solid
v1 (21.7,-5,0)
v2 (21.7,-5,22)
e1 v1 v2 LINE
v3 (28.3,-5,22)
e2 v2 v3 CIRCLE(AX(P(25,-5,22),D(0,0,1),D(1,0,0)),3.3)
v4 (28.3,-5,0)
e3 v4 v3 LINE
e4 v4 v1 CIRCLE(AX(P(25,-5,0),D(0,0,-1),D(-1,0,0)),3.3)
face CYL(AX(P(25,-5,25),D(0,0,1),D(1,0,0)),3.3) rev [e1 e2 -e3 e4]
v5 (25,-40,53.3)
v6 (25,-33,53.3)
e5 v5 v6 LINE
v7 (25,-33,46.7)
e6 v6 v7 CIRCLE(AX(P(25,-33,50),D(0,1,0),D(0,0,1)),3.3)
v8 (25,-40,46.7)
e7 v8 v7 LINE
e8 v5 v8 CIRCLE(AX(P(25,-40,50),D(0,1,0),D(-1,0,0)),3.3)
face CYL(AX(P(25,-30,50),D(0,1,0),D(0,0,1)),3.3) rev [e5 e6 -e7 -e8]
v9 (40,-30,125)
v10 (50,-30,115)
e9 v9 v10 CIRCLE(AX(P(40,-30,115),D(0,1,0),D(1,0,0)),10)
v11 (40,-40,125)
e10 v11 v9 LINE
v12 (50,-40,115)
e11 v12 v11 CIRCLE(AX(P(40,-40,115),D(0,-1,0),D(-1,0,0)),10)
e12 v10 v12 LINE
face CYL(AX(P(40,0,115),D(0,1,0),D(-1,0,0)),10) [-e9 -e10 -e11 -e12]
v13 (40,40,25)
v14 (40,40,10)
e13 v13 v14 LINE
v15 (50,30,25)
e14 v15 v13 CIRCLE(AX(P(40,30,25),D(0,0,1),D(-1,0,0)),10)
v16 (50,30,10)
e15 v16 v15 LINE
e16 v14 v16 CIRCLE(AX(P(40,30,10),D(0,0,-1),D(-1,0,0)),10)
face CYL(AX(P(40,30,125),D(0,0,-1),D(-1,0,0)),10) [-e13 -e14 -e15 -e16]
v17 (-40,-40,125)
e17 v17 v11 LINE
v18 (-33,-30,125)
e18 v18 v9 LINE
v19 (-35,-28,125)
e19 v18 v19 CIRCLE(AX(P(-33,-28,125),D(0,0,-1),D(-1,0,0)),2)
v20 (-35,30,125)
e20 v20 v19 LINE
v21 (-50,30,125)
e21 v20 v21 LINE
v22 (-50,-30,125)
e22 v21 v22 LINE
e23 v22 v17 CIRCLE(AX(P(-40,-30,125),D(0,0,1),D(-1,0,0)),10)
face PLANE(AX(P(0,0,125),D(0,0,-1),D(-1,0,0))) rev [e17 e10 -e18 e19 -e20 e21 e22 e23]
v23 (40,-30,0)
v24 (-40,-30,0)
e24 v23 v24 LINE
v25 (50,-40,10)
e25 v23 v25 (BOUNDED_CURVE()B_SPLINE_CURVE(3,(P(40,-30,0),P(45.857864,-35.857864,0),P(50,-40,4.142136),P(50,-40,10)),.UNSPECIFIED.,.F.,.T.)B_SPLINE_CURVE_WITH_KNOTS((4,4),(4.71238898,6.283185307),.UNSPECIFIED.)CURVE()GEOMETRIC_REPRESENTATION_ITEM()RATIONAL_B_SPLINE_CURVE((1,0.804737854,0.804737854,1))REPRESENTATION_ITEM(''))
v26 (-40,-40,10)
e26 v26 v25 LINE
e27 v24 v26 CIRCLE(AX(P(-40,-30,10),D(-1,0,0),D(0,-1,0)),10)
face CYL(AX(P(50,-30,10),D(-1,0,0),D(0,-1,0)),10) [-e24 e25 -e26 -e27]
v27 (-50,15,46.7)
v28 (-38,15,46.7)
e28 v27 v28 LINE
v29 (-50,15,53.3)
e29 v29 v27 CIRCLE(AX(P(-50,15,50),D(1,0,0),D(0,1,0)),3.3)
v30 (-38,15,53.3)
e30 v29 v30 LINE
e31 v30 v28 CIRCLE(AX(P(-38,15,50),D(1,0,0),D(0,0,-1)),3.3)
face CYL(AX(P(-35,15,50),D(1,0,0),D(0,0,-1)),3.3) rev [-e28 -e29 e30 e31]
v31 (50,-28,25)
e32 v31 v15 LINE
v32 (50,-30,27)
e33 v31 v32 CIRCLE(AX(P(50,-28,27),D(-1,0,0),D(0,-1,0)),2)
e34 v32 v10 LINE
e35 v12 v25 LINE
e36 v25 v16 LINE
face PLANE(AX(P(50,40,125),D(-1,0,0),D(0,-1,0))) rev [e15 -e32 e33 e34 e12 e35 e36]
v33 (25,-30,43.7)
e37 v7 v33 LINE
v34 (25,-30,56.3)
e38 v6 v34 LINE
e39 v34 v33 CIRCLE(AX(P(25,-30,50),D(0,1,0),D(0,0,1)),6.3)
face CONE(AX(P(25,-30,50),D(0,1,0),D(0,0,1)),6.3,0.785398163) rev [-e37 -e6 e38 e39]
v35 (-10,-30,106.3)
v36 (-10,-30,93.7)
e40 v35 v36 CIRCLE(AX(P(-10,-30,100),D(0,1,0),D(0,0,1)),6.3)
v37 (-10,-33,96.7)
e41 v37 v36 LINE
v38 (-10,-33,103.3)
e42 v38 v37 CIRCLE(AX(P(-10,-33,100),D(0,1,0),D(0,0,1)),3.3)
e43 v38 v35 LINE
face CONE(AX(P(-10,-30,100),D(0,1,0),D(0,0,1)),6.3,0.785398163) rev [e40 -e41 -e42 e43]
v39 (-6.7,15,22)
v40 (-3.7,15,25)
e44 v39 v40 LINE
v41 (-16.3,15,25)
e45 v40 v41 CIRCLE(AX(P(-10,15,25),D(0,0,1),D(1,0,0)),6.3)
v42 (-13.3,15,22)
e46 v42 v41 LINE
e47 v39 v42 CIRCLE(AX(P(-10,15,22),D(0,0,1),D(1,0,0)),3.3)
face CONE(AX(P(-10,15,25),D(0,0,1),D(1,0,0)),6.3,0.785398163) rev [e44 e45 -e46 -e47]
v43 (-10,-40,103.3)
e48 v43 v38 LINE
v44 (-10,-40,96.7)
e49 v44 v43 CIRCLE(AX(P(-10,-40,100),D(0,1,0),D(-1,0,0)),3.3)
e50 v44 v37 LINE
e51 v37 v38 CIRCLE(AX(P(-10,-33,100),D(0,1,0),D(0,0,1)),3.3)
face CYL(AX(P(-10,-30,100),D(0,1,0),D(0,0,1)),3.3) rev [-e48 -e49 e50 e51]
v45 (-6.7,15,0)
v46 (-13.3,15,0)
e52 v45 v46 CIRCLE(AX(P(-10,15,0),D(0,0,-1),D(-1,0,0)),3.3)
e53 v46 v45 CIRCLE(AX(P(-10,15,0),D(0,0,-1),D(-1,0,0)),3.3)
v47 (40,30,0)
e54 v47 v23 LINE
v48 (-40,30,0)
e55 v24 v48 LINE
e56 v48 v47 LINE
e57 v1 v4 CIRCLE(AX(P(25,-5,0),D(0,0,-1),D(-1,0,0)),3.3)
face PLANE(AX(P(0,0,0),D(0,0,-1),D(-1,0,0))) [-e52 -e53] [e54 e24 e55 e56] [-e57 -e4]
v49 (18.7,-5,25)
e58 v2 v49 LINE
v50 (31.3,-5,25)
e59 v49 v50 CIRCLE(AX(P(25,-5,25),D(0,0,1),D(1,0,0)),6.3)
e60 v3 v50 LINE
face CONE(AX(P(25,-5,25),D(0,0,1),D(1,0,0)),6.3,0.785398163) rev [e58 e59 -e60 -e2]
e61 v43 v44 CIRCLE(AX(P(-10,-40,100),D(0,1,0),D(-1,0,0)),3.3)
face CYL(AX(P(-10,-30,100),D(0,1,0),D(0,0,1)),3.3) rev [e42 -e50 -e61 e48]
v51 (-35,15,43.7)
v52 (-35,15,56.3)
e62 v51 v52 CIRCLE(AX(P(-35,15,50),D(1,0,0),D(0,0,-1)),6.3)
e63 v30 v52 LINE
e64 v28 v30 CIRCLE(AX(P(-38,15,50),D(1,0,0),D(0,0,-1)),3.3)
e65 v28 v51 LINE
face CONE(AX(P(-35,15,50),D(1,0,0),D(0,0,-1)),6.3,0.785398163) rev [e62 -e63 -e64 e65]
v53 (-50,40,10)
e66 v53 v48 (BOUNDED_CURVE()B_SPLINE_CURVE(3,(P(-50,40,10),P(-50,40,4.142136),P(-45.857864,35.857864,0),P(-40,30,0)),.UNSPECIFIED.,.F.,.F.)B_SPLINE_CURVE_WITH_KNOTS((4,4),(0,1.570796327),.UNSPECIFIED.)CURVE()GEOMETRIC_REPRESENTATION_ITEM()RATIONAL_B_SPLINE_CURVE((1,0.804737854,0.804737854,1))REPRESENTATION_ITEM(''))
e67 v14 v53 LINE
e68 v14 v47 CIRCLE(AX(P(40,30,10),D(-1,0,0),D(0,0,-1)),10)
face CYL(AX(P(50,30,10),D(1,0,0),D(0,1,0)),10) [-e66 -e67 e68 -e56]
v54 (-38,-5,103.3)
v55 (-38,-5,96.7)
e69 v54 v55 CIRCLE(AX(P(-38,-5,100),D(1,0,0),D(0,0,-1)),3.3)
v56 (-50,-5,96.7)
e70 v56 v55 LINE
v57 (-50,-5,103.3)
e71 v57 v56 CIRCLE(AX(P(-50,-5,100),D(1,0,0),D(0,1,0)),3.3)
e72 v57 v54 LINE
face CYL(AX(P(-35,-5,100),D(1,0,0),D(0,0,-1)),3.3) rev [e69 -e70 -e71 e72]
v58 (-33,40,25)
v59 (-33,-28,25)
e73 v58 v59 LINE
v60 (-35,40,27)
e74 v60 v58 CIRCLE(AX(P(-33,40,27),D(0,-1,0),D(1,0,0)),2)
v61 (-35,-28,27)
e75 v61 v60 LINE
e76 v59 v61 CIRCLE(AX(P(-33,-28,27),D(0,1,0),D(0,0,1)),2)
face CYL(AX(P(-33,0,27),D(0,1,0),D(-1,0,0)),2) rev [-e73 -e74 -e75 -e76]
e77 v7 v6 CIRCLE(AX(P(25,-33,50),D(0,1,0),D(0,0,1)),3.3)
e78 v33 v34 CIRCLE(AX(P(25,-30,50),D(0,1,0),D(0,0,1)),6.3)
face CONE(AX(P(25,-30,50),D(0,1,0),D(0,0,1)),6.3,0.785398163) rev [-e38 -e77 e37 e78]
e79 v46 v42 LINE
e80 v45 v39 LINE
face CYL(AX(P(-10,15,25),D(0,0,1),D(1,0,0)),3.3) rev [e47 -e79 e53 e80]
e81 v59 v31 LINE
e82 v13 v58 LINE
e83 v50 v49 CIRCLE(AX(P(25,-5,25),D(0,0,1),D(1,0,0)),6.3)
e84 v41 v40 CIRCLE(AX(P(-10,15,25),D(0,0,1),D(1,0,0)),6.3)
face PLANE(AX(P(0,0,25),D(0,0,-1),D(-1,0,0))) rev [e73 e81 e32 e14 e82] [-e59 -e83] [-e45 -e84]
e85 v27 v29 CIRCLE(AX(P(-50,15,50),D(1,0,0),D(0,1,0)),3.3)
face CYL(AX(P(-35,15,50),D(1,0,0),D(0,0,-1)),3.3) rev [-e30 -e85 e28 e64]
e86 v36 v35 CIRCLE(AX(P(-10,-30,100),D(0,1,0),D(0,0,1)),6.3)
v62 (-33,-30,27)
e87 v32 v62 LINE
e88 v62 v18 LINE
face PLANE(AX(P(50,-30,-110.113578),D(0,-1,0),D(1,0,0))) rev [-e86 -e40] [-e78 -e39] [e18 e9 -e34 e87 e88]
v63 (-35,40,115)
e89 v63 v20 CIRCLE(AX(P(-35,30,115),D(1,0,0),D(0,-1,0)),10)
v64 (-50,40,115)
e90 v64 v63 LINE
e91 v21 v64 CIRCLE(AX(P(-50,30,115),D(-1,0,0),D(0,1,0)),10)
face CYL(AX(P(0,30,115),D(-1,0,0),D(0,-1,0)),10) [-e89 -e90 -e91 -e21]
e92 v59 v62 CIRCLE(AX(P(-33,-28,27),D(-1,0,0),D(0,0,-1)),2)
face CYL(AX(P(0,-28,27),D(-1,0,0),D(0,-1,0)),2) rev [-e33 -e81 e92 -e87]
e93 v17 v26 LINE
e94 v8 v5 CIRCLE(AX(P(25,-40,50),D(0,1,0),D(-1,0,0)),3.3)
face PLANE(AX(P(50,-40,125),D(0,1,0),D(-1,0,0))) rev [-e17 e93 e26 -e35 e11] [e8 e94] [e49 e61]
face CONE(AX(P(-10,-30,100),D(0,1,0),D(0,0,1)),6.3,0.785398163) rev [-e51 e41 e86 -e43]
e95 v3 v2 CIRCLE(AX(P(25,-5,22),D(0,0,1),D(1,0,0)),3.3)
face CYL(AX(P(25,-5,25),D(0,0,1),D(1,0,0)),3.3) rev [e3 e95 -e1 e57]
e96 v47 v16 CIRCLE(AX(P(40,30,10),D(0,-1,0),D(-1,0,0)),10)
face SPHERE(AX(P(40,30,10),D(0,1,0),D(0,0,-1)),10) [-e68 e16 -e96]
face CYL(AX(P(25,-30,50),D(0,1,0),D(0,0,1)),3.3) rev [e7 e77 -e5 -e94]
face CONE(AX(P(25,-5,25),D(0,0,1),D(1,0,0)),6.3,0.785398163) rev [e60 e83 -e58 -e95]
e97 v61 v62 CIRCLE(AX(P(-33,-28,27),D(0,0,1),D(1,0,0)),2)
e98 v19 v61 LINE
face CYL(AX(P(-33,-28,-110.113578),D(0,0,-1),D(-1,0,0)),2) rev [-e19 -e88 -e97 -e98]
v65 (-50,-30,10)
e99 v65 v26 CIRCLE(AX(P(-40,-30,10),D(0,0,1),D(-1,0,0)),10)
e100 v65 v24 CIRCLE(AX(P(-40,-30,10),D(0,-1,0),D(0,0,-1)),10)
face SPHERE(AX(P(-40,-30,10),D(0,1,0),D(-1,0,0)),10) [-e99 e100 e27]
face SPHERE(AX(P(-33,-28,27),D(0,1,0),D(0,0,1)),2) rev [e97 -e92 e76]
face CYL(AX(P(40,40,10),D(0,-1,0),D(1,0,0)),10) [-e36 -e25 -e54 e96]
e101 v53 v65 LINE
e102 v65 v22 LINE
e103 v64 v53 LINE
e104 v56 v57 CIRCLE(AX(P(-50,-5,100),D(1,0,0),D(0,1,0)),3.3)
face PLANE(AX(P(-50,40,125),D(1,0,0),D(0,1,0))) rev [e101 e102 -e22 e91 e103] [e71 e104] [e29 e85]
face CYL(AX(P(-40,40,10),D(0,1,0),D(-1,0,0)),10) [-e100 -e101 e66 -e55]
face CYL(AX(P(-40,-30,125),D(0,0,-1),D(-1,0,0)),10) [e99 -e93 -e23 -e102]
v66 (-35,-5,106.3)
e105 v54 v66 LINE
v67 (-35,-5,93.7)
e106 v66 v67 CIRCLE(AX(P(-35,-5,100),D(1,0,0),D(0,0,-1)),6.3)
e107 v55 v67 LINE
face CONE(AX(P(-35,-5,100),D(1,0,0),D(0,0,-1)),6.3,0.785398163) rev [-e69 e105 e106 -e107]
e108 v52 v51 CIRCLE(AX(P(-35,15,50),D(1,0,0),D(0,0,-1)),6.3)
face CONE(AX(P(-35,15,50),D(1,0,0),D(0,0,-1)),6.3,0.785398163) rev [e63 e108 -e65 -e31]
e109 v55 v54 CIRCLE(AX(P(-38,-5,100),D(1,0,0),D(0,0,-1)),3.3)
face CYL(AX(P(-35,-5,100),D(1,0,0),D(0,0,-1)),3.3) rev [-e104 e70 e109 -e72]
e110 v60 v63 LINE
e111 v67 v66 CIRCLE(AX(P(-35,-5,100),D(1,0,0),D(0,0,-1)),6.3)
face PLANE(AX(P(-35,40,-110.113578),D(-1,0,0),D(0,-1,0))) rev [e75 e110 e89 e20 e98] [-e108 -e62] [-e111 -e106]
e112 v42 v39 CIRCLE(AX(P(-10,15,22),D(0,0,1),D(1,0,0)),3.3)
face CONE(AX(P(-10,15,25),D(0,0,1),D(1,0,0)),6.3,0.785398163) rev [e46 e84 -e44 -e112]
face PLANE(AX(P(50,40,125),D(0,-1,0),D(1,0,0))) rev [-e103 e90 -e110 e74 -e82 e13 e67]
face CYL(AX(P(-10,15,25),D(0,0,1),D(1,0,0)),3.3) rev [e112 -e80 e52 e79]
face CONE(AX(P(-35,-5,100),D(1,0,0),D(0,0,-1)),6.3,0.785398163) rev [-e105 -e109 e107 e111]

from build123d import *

# Parameters (mm, degrees)
BRACKET_L_PROFILE_SKETCH_W                   = 100
BRACKET_L_PROFILE_SKETCH_H                   = 80
BRACKET_BODY_DEPTH                           = 125
RECTANGULAR_CUT_SKETCH_10X15_W               = 85
RECTANGULAR_CUT_SKETCH_10X15_H               = 70
RECTANGULAR_CUT_10X15_DEPTH                  = 100
COUNTERSUNK_HOLES_6XM6_D                     = 6.6
COUNTERSUNK_HOLES_6XM6_DEPTH                 = 36.017159957
COUNTERSUNK_HOLES_6XM6_CSINK_D               = 12.6
COUNTERSUNK_HOLES_6XM6_CSINK_ANGLE           = 90
COUNTERSUNK_HOLES_6XM6_TIP                   = 1.982840043
COUNTERSUNK_HOLES_6XM6_ON_FACE_2_D           = 6.6
COUNTERSUNK_HOLES_6XM6_ON_FACE_2_DEPTH       = 36.017159957
COUNTERSUNK_HOLES_6XM6_ON_FACE_2_CSINK_D     = 12.6
COUNTERSUNK_HOLES_6XM6_ON_FACE_2_CSINK_ANGLE = 90
COUNTERSUNK_HOLES_6XM6_ON_FACE_2_TIP         = 1.982840043
COUNTERSUNK_HOLES_6XM6_ON_FACE_3_D           = 6.6
COUNTERSUNK_HOLES_6XM6_ON_FACE_3_DEPTH       = 36.017159957
COUNTERSUNK_HOLES_6XM6_ON_FACE_3_CSINK_D     = 12.6
COUNTERSUNK_HOLES_6XM6_ON_FACE_3_CSINK_ANGLE = 90
COUNTERSUNK_HOLES_6XM6_ON_FACE_3_TIP         = 1.982840043
OUTER_EDGE_FILLETS_R10_R                     = 10
EDGE_FILLETS_R2_R                            = 2


with BuildPart() as part:
    # Bracket L-Profile Sketch → Bracket Body (new body)
    with BuildSketch(Plane.XY):
        Rectangle(BRACKET_L_PROFILE_SKETCH_W, BRACKET_L_PROFILE_SKETCH_H)
    extrude(amount=BRACKET_BODY_DEPTH)

    # Rectangular Cut Sketch 10x15 → Rectangular Cut 10x15 (cut)
    with BuildSketch(Plane.XY.offset(125)):
        with Locations((7.5, 5)):
            Rectangle(RECTANGULAR_CUT_SKETCH_10X15_W, RECTANGULAR_CUT_SKETCH_10X15_H)
    extrude(amount=-RECTANGULAR_CUT_10X15_DEPTH, mode=Mode.SUBTRACT)

    # Countersunk Holes 6xM6
    with Locations(Plane(origin=(-35, -5, 100), x_dir=(0, 1, 0), z_dir=(1, 0, 0))):
        with Locations((0, 0), (20, -50)):
            CounterSinkHole(COUNTERSUNK_HOLES_6XM6_D / 2, COUNTERSUNK_HOLES_6XM6_CSINK_D / 2, depth=COUNTERSUNK_HOLES_6XM6_DEPTH, counter_sink_angle=COUNTERSUNK_HOLES_6XM6_CSINK_ANGLE)
            with Locations((0, 0, -(COUNTERSUNK_HOLES_6XM6_DEPTH + COUNTERSUNK_HOLES_6XM6_TIP / 2))):  # 118° drill point
                Cone(0, COUNTERSUNK_HOLES_6XM6_D / 2, COUNTERSUNK_HOLES_6XM6_TIP, mode=Mode.SUBTRACT)

    # Countersunk Holes 6xM6 on face 2
    with Locations(Plane(origin=(-10, -30, 100), x_dir=(0, 0, 1), z_dir=(0, 1, 0))):
        with Locations((0, 0), (-50, 35)):
            CounterSinkHole(COUNTERSUNK_HOLES_6XM6_ON_FACE_2_D / 2, COUNTERSUNK_HOLES_6XM6_ON_FACE_2_CSINK_D / 2, depth=COUNTERSUNK_HOLES_6XM6_ON_FACE_2_DEPTH, counter_sink_angle=COUNTERSUNK_HOLES_6XM6_ON_FACE_2_CSINK_ANGLE)
            with Locations((0, 0, -(COUNTERSUNK_HOLES_6XM6_ON_FACE_2_DEPTH + COUNTERSUNK_HOLES_6XM6_ON_FACE_2_TIP / 2))):  # 118° drill point
                Cone(0, COUNTERSUNK_HOLES_6XM6_ON_FACE_2_D / 2, COUNTERSUNK_HOLES_6XM6_ON_FACE_2_TIP, mode=Mode.SUBTRACT)

    # Countersunk Holes 6xM6 on face 3
    with Locations(Plane(origin=(25, -5, 25), x_dir=(1, 0, 0), z_dir=(0, 0, 1))):
        with Locations((0, 0), (-35, 20)):
            CounterSinkHole(COUNTERSUNK_HOLES_6XM6_ON_FACE_3_D / 2, COUNTERSUNK_HOLES_6XM6_ON_FACE_3_CSINK_D / 2, depth=COUNTERSUNK_HOLES_6XM6_ON_FACE_3_DEPTH, counter_sink_angle=COUNTERSUNK_HOLES_6XM6_ON_FACE_3_CSINK_ANGLE)
            with Locations((0, 0, -(COUNTERSUNK_HOLES_6XM6_ON_FACE_3_DEPTH + COUNTERSUNK_HOLES_6XM6_ON_FACE_3_TIP / 2))):  # 118° drill point
                Cone(0, COUNTERSUNK_HOLES_6XM6_ON_FACE_3_D / 2, COUNTERSUNK_HOLES_6XM6_ON_FACE_3_TIP, mode=Mode.SUBTRACT)

    # Outer Edge Fillets R10
    outer_edge_fillets_r10_edges = [part.edges().sort_by_distance(p)[0] for p in [
        (50, -35, 125),
        (-42.5, 40, 125),
        (50, 40, 12.5),
        (0, 40, 0),
        (50, 0, 0),
        (0, -40, 0),
        (-50, 0, 0),
        (-50, -40, 62.5),
    ]]
    fillet(outer_edge_fillets_r10_edges, radius=OUTER_EDGE_FILLETS_R10_R)

    # Edge Fillets R2
    edge_fillets_r2_edges = [part.edges().sort_by_distance(p)[0] for p in [
        (-35, 5, 25),
        (-35, -30, 75),
        (7.5, -30, 25),
    ]]
    fillet(edge_fillets_r2_edges, radius=EDGE_FILLETS_R2_R)


solid = part.part
